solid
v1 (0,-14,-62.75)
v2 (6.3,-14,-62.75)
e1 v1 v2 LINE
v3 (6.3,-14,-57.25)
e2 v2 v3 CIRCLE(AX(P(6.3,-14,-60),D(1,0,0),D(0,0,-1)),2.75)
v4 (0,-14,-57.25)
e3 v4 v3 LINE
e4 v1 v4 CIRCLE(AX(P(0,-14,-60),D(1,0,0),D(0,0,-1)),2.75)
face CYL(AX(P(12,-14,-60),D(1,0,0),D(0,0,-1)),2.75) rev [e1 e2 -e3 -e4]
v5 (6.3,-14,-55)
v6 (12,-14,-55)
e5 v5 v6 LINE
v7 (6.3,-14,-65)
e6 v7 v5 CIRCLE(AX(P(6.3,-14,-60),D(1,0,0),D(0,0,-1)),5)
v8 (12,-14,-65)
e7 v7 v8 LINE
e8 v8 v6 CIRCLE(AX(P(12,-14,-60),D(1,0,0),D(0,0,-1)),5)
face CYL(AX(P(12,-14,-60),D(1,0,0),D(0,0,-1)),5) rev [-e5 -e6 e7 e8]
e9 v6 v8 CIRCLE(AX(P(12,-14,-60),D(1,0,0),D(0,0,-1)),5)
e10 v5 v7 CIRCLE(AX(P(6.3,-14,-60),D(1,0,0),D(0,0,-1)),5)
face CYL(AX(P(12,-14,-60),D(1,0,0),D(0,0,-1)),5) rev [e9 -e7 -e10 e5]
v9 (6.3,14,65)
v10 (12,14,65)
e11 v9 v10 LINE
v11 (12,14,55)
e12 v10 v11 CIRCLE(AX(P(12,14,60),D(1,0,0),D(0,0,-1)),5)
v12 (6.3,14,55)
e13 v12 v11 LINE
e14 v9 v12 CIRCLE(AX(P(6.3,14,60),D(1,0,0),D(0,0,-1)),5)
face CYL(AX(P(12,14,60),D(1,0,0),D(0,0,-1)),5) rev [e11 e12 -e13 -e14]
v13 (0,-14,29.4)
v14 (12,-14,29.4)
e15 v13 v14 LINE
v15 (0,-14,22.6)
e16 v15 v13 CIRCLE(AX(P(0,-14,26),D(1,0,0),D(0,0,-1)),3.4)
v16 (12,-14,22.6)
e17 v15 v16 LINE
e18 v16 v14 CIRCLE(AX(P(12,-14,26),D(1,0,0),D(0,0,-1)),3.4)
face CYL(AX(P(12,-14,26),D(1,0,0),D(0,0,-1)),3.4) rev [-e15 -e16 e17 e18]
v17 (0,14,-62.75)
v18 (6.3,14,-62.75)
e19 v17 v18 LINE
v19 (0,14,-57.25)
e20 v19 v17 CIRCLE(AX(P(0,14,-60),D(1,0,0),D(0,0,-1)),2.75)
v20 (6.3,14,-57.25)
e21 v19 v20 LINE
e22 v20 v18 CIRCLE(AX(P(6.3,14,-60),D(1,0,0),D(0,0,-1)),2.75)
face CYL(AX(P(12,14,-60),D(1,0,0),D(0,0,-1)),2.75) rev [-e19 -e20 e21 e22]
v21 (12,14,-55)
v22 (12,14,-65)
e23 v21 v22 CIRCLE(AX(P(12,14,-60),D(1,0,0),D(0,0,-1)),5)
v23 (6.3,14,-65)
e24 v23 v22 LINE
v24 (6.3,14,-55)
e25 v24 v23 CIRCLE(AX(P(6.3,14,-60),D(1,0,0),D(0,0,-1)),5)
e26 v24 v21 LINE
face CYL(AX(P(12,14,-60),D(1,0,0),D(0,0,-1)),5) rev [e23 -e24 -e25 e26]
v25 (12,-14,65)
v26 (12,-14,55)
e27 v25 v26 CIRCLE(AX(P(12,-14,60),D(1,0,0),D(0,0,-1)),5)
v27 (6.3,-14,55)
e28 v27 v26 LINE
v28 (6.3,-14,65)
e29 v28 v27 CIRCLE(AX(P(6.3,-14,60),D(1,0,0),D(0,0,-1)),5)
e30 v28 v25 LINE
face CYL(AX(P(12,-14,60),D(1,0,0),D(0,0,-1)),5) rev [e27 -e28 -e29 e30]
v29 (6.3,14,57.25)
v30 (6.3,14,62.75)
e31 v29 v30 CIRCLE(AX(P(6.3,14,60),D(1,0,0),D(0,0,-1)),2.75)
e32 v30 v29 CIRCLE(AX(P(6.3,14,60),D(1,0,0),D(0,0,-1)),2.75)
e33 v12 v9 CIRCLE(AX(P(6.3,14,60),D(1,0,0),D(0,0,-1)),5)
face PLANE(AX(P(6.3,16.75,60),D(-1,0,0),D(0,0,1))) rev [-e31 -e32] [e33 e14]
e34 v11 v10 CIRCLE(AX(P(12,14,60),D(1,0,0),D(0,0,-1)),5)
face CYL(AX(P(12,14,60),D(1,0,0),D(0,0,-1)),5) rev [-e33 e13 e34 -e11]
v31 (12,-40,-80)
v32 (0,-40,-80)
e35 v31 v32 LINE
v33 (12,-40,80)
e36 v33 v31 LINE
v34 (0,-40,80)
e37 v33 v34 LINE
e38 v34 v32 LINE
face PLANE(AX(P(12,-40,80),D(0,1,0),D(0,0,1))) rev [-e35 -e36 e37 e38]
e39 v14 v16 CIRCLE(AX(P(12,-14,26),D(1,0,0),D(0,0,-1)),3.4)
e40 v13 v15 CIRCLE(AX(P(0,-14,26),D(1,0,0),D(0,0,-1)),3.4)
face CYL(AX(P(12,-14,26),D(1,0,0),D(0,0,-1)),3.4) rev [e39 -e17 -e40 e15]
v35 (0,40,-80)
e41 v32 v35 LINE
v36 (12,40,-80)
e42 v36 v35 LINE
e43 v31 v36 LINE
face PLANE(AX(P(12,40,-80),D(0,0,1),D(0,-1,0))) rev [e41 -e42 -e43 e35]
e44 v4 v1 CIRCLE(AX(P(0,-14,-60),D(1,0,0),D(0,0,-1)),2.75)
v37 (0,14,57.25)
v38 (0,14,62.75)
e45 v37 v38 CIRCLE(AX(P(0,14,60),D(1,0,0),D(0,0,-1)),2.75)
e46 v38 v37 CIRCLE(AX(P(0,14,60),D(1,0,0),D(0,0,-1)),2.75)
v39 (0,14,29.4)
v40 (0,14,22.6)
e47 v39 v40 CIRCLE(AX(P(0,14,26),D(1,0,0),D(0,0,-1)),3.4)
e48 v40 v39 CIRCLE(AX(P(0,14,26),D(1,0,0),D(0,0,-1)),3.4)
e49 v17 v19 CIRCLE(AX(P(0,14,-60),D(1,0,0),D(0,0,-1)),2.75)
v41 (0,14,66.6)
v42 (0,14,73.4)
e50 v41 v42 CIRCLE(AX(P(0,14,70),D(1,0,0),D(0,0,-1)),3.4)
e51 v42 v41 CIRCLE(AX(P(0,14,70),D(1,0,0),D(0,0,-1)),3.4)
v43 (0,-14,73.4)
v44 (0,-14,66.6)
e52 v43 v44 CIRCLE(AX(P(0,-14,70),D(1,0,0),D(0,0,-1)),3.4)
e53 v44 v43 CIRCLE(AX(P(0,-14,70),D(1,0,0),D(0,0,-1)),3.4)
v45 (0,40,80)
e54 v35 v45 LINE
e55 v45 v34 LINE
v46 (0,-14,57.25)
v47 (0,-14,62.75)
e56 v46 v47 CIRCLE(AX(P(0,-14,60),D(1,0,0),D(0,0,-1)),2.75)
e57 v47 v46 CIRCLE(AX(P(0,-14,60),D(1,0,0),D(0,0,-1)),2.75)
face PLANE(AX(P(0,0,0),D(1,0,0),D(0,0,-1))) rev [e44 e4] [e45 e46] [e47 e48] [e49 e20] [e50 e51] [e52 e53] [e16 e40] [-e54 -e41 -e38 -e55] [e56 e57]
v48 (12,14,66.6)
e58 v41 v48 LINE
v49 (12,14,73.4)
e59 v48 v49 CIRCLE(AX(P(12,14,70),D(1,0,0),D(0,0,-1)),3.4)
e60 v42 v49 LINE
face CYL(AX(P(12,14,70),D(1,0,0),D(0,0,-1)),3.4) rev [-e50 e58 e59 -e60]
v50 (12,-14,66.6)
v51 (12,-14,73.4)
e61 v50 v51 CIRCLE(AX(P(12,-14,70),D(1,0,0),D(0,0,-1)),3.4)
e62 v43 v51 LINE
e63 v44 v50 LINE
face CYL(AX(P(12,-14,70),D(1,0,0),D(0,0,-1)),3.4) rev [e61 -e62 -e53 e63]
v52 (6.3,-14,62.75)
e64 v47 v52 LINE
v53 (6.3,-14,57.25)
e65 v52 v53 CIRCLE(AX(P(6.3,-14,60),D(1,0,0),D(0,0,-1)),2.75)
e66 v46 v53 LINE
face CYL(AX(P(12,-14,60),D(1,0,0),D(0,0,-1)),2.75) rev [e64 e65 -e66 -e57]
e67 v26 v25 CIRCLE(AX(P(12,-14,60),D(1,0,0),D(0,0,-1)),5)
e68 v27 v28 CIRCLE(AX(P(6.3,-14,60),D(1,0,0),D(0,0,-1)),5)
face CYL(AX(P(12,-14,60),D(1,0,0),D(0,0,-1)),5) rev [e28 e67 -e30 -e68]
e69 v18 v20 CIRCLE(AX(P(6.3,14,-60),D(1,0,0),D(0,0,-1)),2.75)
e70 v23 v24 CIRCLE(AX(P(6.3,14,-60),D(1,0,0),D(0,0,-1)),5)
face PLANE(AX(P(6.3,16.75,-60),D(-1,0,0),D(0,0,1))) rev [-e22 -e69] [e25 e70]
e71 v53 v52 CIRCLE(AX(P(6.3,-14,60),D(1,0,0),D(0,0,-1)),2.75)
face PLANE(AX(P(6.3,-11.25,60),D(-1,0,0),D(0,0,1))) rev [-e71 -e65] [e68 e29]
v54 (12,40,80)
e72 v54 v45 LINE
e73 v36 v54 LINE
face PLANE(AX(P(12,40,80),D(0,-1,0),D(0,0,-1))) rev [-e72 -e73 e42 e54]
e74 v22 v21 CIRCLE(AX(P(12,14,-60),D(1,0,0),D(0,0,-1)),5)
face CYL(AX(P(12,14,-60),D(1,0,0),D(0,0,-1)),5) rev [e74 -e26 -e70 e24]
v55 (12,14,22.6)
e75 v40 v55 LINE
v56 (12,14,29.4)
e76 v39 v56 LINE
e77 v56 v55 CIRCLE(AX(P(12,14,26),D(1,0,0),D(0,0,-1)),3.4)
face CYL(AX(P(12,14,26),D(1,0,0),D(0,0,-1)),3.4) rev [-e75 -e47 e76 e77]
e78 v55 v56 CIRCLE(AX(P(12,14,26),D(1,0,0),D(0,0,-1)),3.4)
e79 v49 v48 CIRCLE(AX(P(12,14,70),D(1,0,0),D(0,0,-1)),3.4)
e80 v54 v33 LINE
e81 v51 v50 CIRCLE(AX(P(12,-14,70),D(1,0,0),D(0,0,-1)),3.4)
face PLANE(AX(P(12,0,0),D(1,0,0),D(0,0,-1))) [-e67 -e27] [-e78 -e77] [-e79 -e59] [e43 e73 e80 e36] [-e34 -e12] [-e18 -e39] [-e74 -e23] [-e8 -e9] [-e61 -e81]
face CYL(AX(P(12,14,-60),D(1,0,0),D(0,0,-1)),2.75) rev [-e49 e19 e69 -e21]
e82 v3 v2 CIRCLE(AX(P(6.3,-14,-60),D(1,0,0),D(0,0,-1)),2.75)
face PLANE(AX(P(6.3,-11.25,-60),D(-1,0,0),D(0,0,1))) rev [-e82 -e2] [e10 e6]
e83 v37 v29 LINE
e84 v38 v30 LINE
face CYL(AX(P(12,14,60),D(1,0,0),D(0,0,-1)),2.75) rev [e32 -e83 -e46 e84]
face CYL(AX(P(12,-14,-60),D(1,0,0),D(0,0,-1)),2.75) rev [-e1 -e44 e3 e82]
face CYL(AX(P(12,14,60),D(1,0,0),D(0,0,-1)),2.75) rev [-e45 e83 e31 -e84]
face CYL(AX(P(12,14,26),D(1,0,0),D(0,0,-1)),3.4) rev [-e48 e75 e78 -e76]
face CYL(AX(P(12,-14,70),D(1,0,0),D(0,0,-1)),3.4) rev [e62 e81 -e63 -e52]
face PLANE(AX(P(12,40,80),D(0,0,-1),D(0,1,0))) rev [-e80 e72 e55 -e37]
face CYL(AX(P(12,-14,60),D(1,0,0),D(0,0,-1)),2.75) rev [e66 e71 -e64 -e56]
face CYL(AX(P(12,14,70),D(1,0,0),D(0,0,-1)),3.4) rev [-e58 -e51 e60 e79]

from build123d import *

# Parameters (mm, degrees)
SKETCH_1_W                = 160
SKETCH_1_H                = 80
EXTRUDE_1_DEPTH           = 12
HOLE_WIZARD_M8_1_D        = 6.8
HOLE_WIZARD_1_D           = 5.5
HOLE_WIZARD_1_CBORE_D     = 10
HOLE_WIZARD_1_CBORE_DEPTH = 5.7


with BuildPart() as part:
    # 草图1 → 凸台-拉伸1 (new body)
    with BuildSketch(Plane(origin=(0, 0, 0), x_dir=(0, 0, -1), z_dir=(1, 0, 0))):
        Rectangle(SKETCH_1_W, SKETCH_1_H)
    extrude(amount=EXTRUDE_1_DEPTH)

    # M8 螺纹孔1 (through all)
    with Locations(Plane(origin=(12, 0, 0), x_dir=(0, 0, -1), z_dir=(1, 0, 0))):
        with Locations((-70, 14), (-70, -14), (-26, 14), (-26, -14)):
            Hole(HOLE_WIZARD_M8_1_D / 2)

    # 打孔尺寸(%根据)内六角圆柱头螺钉的类型1 (through all)
    with Locations(Plane(origin=(12, 0, 0), x_dir=(0, 0, -1), z_dir=(1, 0, 0))):
        with Locations((-60, 14), (-60, -14), (60, 14), (60, -14)):
            CounterBoreHole(HOLE_WIZARD_1_D / 2, HOLE_WIZARD_1_CBORE_D / 2, HOLE_WIZARD_1_CBORE_DEPTH)


solid = part.part
